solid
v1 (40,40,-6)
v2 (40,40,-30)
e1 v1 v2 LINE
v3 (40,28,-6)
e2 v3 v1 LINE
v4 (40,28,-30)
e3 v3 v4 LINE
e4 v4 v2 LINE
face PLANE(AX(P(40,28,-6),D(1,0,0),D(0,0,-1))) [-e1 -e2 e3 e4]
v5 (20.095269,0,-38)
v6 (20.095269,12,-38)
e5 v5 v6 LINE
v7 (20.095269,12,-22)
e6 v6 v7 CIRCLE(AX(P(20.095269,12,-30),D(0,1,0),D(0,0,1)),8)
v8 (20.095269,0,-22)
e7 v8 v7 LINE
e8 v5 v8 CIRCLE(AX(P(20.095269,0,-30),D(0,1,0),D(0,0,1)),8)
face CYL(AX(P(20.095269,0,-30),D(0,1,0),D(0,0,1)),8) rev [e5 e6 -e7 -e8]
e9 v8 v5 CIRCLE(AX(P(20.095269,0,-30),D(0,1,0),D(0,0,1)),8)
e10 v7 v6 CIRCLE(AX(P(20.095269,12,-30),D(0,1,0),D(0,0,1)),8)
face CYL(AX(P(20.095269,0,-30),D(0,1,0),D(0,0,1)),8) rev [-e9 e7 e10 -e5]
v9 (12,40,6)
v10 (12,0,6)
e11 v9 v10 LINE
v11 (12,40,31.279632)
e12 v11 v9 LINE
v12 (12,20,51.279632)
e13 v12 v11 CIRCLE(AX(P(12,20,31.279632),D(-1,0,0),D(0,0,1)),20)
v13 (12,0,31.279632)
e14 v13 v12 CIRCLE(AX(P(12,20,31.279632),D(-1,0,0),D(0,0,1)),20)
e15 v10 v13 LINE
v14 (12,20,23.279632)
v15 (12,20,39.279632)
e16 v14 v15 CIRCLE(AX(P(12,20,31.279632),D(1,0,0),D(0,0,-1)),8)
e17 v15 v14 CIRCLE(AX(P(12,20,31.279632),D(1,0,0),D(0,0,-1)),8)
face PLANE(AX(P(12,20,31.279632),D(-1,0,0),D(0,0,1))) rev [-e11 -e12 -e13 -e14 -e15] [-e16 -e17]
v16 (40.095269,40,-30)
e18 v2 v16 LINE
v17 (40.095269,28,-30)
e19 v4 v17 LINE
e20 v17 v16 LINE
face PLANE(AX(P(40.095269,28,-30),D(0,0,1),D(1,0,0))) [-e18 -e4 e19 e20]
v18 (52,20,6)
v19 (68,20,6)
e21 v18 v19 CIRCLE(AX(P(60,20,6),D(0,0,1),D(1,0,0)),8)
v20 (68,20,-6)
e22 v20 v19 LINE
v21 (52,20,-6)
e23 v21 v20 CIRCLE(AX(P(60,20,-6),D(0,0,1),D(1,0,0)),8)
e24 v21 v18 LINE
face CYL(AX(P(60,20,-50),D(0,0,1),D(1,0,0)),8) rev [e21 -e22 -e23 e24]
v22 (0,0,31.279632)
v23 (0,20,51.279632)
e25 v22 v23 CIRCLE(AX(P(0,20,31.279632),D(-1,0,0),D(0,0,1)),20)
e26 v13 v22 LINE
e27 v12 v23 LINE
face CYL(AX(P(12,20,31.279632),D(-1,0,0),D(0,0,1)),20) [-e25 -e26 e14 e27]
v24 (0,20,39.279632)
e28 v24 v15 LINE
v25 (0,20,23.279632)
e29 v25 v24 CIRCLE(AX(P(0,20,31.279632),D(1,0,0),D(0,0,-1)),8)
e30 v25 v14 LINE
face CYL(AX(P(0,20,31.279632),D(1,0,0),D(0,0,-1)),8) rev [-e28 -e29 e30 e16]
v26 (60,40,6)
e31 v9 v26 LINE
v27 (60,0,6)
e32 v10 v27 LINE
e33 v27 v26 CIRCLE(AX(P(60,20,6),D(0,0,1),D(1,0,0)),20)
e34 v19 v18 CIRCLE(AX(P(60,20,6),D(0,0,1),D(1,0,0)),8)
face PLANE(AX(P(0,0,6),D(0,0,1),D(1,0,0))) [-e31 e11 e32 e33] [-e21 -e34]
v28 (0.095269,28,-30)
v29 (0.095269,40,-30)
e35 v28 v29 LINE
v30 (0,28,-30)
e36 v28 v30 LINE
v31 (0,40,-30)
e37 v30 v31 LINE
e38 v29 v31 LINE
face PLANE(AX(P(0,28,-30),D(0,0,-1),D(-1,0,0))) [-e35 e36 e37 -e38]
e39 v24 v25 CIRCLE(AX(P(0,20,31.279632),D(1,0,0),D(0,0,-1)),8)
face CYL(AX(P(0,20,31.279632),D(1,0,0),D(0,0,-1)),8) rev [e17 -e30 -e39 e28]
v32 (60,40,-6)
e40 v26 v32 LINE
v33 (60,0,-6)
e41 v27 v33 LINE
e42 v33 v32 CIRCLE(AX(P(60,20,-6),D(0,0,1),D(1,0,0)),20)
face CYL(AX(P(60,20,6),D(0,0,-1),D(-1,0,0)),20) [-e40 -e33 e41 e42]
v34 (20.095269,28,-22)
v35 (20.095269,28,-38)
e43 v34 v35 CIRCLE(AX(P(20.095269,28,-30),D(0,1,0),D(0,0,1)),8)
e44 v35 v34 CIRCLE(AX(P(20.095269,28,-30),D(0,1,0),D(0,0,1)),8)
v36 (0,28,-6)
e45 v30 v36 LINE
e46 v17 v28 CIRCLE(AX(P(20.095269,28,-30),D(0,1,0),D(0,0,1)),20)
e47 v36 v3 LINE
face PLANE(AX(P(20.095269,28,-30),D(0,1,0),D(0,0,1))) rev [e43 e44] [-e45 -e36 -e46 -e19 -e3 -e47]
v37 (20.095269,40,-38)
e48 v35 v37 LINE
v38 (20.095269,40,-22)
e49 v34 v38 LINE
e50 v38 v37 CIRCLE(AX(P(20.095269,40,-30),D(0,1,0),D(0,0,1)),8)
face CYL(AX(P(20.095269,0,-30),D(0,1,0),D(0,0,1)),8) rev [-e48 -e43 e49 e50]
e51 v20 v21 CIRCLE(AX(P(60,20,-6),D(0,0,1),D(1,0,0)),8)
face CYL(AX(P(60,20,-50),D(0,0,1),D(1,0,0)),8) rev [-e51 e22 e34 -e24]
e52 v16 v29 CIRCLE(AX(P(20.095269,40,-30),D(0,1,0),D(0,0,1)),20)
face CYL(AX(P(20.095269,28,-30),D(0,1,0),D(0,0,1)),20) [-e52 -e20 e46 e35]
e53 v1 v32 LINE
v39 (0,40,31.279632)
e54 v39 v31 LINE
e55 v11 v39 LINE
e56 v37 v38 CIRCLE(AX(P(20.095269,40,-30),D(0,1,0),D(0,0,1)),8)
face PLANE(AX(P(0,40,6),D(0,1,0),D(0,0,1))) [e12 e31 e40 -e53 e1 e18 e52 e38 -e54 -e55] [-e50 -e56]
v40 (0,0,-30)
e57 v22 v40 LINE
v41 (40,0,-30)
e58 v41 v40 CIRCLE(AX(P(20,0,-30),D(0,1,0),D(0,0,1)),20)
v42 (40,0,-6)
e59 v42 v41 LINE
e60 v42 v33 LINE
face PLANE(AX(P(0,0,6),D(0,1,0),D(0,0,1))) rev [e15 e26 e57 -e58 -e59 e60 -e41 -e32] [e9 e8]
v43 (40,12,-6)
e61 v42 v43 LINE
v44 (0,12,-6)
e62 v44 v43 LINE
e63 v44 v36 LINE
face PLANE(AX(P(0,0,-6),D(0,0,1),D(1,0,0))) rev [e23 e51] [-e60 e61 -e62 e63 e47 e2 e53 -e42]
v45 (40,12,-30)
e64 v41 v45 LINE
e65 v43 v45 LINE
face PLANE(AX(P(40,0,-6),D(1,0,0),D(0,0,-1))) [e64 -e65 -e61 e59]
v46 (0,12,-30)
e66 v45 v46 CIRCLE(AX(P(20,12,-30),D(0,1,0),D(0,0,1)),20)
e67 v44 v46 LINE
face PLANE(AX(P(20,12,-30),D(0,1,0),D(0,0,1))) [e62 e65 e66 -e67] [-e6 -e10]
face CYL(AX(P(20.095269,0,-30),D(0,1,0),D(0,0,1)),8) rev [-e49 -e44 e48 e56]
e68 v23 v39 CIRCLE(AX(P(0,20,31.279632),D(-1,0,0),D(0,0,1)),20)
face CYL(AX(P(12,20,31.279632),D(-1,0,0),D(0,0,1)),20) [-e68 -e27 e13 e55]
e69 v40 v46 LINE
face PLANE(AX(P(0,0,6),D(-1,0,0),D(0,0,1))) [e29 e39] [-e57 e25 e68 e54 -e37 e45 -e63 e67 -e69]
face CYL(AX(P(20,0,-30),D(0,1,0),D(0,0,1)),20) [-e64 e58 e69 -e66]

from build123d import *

# Parameters (mm, degrees)
BASE_BRACKET_DEPTH          = 6
UPPER_START                 = -28
UPPER_LUG_PLATE_DEPTH       = 12
UPPER_LUG_ROUNDED_END_DEPTH = 12
UPPER_LUG_HOLE_SKETCH_R     = 8
UPPER_LUG_HOLE_16_DEPTH     = 103.46950766
SIDE_LUG_DEPTH              = 12
SIDE_LUG_HOLE_SKETCH_R      = 8
SIDE_LUG_HOLE_16_DEPTH      = 95.093573716
BASE_HOLE_SKETCH_R          = 8
BASE_HOLE_16_DEPTH          = 106.527247666


with BuildPart() as part:
    # Base Profile Sketch → Base Bracket (new, symmetric)
    with BuildSketch(Plane.XY):
        with BuildLine():
            Line((0, 0), (60, 0))
            ThreePointArc((60, 0), (80, 20), (60, 40))
            Line((60, 40), (0, 40))
            Line((0, 40), (0, 0))
        make_face()
    extrude(amount=BASE_BRACKET_DEPTH, both=True)

    # Upper Lug Plate Sketch → Upper Lug Plate (add)
    with BuildSketch(Plane(origin=(0, 40, 0), x_dir=(1, 0, 0), z_dir=(0, 1, 0)).offset(UPPER_START)):
        with BuildLine():
            Line((0, 6), (40, 6))
            Line((40, 6), (40, 30))
            ThreePointArc((40, 30), (20, 50), (0, 30))
            Line((0, 30), (0, 6))
        make_face()
    extrude(amount=-UPPER_LUG_PLATE_DEPTH)

    # Upper Lug End Sketch → Upper Lug Rounded End (add)
    with BuildSketch(Plane(origin=(0, 40, 0), x_dir=(1, 0, 0), z_dir=(0, 1, 0))):
        with BuildLine():
            Line((40.095269472, 30), (40, 30))
            Line((40, 30), (40, 6))
            Line((40, 6), (0, 6))
            Line((0, 6), (0, 30))
            Line((0, 30), (0.095269472, 30))
            ThreePointArc((0.095269472, 30), (20.095269472, 50), (40.095269472, 30))
        make_face()
    extrude(amount=-UPPER_LUG_ROUNDED_END_DEPTH)

    # Upper Lug Hole Sketch → Upper Lug Hole Ø16 (cut, through all)
    with BuildSketch(Plane(origin=(0, 40, 0), x_dir=(1, 0, 0), z_dir=(0, 1, 0))):
        with Locations(Location((20.095269472, 30, 0), (0, 0, 270))):
            Circle(UPPER_LUG_HOLE_SKETCH_R)
    extrude(amount=-UPPER_LUG_HOLE_16_DEPTH, mode=Mode.SUBTRACT)

    # Side Lug Sketch → Side Lug (add)
    with BuildSketch(Plane.ZY):
        with BuildLine():
            Line((6, 40), (31.279631577, 40))
            ThreePointArc((31.279631577, 40), (51.279631577, 20), (31.279631577, 0))
            Line((31.279631577, 0), (6, 0))
            Line((6, 0), (6, 40))
        make_face()
    extrude(amount=-SIDE_LUG_DEPTH)

    # Side Lug Hole Sketch → Side Lug Hole Ø16 (cut, through all)
    with BuildSketch(Plane(origin=(12, 0, 0), x_dir=(0, 0, -1), z_dir=(1, 0, 0))):
        with Locations((-31.279631577, 20)):
            Circle(SIDE_LUG_HOLE_SKETCH_R)
    extrude(amount=-SIDE_LUG_HOLE_16_DEPTH, mode=Mode.SUBTRACT)

    # Base Hole Sketch → Base Hole Ø16 (cut, through all)
    with BuildSketch(Plane.XY.offset(6)):
        with Locations((60, 20)):
            Circle(BASE_HOLE_SKETCH_R)
    extrude(amount=-BASE_HOLE_16_DEPTH, mode=Mode.SUBTRACT)


solid = part.part
